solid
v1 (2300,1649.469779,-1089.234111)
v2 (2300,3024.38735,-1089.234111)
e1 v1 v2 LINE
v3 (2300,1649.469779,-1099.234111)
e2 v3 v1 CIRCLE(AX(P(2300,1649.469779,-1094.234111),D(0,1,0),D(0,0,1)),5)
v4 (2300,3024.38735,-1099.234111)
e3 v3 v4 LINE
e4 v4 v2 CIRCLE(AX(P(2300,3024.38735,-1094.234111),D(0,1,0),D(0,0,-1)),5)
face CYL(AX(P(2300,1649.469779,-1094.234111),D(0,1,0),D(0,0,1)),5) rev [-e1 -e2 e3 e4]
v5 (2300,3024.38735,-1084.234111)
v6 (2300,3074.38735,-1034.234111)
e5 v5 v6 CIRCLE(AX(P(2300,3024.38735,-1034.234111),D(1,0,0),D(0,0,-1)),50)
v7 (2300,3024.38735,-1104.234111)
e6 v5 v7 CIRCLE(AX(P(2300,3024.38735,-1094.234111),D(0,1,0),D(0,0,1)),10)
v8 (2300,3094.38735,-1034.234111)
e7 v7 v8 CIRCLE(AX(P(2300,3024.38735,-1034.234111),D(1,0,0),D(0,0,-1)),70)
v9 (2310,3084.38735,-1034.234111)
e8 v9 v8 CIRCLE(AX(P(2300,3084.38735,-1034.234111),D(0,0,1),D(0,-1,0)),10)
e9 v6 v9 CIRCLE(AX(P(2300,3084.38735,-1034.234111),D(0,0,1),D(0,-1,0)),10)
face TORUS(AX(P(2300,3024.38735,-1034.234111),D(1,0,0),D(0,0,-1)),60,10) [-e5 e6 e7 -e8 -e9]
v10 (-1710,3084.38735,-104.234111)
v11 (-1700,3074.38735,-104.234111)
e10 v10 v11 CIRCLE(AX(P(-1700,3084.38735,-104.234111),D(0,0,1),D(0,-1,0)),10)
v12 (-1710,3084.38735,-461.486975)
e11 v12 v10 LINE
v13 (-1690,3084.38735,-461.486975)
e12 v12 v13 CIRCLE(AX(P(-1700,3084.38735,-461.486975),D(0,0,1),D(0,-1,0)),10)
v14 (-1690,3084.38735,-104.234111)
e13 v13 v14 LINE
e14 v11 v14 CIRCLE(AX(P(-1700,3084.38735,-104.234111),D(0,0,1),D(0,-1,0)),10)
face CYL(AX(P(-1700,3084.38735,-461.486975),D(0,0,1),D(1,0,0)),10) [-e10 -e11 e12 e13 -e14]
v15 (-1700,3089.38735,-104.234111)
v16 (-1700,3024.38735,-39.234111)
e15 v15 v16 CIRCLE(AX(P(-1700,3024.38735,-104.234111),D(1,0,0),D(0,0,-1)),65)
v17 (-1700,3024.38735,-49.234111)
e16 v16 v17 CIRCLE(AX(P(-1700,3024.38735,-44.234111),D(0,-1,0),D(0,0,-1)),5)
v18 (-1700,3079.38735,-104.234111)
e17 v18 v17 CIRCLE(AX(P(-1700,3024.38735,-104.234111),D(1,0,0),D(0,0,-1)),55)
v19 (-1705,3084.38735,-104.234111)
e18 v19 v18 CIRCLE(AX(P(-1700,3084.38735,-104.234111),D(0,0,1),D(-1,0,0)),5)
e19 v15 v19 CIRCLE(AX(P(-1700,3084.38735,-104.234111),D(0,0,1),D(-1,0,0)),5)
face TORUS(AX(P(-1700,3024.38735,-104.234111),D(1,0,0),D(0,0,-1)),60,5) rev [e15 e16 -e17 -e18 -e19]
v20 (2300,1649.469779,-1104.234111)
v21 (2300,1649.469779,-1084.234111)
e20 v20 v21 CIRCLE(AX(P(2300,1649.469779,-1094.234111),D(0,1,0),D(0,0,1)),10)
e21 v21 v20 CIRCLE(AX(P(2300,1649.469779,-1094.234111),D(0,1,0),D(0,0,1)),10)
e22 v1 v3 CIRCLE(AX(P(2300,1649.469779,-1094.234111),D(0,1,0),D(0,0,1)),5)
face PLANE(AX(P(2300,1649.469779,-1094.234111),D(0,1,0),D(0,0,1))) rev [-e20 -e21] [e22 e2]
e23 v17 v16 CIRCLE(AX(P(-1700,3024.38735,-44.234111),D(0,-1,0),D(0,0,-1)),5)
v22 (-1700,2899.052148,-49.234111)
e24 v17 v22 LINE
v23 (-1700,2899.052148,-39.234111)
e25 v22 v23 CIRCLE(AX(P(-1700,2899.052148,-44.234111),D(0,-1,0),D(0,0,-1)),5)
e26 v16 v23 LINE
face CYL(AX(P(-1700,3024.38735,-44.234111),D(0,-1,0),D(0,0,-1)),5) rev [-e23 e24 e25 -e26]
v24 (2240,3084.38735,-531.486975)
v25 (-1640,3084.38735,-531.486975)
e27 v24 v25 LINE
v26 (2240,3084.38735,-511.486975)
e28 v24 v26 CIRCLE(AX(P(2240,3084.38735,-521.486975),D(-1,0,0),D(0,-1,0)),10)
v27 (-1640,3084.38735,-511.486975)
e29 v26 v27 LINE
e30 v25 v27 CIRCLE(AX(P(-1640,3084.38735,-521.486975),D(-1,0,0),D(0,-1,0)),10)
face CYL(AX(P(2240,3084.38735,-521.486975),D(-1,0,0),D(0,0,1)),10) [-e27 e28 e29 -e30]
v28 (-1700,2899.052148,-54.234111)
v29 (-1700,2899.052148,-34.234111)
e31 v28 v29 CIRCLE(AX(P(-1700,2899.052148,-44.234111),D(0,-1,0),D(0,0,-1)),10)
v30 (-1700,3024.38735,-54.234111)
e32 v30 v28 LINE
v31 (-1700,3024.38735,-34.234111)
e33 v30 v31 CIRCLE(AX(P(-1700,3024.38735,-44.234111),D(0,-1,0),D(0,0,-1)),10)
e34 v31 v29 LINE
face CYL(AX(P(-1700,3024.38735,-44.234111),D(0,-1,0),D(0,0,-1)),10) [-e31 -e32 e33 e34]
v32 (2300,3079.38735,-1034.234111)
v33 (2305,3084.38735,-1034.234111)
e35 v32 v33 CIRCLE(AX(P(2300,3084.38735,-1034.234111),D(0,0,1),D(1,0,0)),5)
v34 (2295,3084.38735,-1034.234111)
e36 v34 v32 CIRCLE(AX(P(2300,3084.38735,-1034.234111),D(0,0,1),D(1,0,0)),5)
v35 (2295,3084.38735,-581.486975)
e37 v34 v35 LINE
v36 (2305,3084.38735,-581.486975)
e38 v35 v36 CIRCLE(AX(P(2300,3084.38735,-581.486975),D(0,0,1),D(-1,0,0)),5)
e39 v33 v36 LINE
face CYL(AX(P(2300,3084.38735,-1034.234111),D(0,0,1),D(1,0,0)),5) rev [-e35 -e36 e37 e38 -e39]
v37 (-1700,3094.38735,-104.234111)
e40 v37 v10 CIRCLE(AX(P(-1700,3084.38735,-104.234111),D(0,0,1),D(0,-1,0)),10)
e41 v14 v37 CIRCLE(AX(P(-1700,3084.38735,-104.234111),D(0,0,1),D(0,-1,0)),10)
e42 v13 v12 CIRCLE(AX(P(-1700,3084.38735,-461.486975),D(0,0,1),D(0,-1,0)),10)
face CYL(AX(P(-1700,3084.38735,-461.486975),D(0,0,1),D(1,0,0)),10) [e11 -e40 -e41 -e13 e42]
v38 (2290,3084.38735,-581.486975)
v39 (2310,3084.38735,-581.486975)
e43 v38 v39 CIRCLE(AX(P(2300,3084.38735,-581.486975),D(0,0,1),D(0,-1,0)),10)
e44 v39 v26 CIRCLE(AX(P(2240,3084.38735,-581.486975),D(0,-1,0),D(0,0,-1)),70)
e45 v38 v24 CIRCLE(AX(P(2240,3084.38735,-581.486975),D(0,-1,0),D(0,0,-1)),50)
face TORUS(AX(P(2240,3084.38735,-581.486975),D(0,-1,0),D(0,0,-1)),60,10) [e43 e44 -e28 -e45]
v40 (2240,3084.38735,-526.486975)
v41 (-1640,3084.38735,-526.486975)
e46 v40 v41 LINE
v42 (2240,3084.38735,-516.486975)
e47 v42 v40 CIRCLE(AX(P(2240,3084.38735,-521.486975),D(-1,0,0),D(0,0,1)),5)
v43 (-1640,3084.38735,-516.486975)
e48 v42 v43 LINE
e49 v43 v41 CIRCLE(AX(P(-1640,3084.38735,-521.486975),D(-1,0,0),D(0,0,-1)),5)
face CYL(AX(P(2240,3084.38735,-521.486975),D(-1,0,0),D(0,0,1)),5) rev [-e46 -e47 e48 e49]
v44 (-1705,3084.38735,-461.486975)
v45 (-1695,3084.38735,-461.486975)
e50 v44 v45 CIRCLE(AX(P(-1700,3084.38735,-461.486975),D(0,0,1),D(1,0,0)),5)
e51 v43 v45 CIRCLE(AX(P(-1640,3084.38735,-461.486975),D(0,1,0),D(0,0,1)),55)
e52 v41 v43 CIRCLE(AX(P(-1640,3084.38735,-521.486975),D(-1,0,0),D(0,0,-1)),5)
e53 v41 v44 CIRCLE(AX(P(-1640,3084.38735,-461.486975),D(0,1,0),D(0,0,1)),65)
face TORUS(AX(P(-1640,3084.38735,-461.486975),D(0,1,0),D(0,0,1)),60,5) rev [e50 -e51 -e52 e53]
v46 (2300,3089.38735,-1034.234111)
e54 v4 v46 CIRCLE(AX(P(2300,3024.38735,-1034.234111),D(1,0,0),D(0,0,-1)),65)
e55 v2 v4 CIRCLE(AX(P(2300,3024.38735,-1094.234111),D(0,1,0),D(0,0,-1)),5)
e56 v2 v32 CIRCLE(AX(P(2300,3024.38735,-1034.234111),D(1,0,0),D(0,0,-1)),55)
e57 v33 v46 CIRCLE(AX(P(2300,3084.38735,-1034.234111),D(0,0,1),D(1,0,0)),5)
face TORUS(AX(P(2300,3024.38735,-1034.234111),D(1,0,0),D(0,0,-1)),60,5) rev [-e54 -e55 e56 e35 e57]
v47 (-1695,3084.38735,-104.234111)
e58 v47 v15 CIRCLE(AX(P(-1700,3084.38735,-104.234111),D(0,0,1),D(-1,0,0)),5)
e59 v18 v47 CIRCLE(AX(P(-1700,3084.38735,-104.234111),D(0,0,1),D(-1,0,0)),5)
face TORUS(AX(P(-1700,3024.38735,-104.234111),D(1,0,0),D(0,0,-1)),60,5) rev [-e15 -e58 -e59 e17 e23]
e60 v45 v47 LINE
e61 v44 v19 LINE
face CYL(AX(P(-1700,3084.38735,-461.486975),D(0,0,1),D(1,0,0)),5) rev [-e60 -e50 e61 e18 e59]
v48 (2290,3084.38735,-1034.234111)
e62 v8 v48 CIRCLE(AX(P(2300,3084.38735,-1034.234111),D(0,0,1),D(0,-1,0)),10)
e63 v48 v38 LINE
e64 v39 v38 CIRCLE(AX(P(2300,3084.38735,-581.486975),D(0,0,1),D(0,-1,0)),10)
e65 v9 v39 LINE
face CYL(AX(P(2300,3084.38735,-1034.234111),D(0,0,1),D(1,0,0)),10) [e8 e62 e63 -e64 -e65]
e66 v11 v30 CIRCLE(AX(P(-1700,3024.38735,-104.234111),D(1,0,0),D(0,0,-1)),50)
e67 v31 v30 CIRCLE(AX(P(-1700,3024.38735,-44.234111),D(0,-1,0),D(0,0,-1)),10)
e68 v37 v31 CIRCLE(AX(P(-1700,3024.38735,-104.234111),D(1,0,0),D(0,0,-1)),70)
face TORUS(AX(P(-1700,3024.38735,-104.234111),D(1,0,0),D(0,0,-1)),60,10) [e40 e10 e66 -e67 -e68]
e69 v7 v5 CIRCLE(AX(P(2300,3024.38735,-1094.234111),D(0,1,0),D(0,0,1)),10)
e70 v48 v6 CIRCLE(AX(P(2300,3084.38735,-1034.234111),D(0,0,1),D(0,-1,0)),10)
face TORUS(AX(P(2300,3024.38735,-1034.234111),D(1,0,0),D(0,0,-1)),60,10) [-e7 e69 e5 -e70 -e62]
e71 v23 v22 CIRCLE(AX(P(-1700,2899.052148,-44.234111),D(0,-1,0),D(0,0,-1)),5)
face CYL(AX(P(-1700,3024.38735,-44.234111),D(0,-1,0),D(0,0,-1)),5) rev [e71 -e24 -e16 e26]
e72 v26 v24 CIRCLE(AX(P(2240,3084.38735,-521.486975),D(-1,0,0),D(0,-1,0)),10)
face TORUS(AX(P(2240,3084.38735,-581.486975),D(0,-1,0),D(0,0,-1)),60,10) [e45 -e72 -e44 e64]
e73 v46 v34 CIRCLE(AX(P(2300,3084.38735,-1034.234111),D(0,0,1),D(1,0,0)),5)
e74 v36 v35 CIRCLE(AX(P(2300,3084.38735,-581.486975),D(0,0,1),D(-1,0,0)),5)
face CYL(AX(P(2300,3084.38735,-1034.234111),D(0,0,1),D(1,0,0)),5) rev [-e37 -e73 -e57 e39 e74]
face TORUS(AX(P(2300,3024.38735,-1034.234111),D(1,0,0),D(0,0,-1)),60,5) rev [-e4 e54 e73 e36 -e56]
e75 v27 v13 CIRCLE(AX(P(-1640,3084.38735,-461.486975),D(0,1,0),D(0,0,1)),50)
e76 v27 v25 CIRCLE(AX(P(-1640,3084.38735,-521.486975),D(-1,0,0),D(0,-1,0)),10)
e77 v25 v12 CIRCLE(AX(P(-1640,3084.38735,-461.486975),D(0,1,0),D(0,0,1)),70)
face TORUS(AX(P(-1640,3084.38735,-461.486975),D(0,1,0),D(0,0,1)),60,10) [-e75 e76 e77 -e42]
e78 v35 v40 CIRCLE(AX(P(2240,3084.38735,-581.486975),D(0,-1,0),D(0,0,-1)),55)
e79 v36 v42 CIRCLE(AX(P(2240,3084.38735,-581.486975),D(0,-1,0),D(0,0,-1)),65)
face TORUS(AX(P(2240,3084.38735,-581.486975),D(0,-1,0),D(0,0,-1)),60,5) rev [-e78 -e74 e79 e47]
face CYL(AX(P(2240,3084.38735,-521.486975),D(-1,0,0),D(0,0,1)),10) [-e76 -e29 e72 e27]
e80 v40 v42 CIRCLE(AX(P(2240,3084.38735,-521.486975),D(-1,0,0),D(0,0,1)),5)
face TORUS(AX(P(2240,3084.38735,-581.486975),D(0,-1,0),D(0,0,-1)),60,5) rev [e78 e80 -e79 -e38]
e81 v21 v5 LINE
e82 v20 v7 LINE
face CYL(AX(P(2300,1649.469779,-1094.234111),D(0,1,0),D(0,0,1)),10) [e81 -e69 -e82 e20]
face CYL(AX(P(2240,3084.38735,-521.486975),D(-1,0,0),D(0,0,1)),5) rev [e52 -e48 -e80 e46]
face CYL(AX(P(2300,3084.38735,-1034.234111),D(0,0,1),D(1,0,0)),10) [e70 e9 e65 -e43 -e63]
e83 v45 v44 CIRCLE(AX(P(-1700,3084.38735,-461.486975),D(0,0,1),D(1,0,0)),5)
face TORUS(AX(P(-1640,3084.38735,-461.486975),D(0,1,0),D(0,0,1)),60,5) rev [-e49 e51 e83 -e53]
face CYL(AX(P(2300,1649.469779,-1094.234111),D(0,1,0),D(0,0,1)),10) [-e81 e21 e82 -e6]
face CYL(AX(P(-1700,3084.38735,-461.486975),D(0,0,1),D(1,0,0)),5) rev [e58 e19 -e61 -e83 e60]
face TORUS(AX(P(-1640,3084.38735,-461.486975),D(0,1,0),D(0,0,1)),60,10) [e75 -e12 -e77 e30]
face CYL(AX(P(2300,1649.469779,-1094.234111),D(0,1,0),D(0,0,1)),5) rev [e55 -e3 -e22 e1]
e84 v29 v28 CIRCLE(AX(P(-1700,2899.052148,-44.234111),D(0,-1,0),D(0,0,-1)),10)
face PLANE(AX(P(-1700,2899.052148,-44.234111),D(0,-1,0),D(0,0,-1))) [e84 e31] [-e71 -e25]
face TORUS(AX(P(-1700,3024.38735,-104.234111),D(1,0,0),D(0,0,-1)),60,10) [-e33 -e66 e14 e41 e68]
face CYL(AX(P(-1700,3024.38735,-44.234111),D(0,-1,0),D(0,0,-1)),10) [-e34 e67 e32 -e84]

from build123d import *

# Parameters (mm, degrees)
SWEEP_THIN1_PROFILE_R   = 10
SWEEP_THIN1_PROFILE_R_2 = 5


with BuildPart() as part:
    # Sweep-Thin1: sweep along a curve in space
    with BuildLine() as sweep_thin1_path:
        Line((-1700, 2899.052148193, -44.234110711), (-1700, 3024.387350178, -44.234110711))
        ThreePointArc((-1700, 3024.387350178, -44.234110711), (-1700, 3066.813757049, -61.80770384), (-1700, 3084.387350178, -104.234110711))
        Line((-1700, 3084.387350178, -104.234110711), (-1700, 3084.387350178, -461.486974567))
        ThreePointArc((-1700, 3084.387350178, -461.486974567), (-1682.426406871, 3084.387350178, -503.913381439), (-1640, 3084.387350178, -521.486974567))
        Line((-1640, 3084.387350178, -521.486974567), (2240, 3084.387350178, -521.486974567))
        ThreePointArc((2300, 3084.387350178, -581.486974567), (2282.426406871, 3084.387350178, -539.060567696), (2240, 3084.387350178, -521.486974567))
        Line((2300, 3084.387350178, -1034.234110711), (2300, 3084.387350178, -581.486974567))
        ThreePointArc((2300, 3024.387350178, -1094.234110711), (2300, 3066.813757049, -1076.660517582), (2300, 3084.387350178, -1034.234110711))
        Line((2300, 1649.469779319, -1094.234110711), (2300, 3024.387350178, -1094.234110711))
    # Sweep-Thin1 profile (on start of the path) → Sweep-Thin1 (sweep)
    with BuildSketch(Plane(origin=(-1700, 2899.052148193, -44.234110711), x_dir=(0, 0, 1), z_dir=(0, 1, 0))):
        Circle(SWEEP_THIN1_PROFILE_R)
        Circle(SWEEP_THIN1_PROFILE_R_2, mode=Mode.SUBTRACT)
    sweep(path=sweep_thin1_path.line)


solid = part.part
